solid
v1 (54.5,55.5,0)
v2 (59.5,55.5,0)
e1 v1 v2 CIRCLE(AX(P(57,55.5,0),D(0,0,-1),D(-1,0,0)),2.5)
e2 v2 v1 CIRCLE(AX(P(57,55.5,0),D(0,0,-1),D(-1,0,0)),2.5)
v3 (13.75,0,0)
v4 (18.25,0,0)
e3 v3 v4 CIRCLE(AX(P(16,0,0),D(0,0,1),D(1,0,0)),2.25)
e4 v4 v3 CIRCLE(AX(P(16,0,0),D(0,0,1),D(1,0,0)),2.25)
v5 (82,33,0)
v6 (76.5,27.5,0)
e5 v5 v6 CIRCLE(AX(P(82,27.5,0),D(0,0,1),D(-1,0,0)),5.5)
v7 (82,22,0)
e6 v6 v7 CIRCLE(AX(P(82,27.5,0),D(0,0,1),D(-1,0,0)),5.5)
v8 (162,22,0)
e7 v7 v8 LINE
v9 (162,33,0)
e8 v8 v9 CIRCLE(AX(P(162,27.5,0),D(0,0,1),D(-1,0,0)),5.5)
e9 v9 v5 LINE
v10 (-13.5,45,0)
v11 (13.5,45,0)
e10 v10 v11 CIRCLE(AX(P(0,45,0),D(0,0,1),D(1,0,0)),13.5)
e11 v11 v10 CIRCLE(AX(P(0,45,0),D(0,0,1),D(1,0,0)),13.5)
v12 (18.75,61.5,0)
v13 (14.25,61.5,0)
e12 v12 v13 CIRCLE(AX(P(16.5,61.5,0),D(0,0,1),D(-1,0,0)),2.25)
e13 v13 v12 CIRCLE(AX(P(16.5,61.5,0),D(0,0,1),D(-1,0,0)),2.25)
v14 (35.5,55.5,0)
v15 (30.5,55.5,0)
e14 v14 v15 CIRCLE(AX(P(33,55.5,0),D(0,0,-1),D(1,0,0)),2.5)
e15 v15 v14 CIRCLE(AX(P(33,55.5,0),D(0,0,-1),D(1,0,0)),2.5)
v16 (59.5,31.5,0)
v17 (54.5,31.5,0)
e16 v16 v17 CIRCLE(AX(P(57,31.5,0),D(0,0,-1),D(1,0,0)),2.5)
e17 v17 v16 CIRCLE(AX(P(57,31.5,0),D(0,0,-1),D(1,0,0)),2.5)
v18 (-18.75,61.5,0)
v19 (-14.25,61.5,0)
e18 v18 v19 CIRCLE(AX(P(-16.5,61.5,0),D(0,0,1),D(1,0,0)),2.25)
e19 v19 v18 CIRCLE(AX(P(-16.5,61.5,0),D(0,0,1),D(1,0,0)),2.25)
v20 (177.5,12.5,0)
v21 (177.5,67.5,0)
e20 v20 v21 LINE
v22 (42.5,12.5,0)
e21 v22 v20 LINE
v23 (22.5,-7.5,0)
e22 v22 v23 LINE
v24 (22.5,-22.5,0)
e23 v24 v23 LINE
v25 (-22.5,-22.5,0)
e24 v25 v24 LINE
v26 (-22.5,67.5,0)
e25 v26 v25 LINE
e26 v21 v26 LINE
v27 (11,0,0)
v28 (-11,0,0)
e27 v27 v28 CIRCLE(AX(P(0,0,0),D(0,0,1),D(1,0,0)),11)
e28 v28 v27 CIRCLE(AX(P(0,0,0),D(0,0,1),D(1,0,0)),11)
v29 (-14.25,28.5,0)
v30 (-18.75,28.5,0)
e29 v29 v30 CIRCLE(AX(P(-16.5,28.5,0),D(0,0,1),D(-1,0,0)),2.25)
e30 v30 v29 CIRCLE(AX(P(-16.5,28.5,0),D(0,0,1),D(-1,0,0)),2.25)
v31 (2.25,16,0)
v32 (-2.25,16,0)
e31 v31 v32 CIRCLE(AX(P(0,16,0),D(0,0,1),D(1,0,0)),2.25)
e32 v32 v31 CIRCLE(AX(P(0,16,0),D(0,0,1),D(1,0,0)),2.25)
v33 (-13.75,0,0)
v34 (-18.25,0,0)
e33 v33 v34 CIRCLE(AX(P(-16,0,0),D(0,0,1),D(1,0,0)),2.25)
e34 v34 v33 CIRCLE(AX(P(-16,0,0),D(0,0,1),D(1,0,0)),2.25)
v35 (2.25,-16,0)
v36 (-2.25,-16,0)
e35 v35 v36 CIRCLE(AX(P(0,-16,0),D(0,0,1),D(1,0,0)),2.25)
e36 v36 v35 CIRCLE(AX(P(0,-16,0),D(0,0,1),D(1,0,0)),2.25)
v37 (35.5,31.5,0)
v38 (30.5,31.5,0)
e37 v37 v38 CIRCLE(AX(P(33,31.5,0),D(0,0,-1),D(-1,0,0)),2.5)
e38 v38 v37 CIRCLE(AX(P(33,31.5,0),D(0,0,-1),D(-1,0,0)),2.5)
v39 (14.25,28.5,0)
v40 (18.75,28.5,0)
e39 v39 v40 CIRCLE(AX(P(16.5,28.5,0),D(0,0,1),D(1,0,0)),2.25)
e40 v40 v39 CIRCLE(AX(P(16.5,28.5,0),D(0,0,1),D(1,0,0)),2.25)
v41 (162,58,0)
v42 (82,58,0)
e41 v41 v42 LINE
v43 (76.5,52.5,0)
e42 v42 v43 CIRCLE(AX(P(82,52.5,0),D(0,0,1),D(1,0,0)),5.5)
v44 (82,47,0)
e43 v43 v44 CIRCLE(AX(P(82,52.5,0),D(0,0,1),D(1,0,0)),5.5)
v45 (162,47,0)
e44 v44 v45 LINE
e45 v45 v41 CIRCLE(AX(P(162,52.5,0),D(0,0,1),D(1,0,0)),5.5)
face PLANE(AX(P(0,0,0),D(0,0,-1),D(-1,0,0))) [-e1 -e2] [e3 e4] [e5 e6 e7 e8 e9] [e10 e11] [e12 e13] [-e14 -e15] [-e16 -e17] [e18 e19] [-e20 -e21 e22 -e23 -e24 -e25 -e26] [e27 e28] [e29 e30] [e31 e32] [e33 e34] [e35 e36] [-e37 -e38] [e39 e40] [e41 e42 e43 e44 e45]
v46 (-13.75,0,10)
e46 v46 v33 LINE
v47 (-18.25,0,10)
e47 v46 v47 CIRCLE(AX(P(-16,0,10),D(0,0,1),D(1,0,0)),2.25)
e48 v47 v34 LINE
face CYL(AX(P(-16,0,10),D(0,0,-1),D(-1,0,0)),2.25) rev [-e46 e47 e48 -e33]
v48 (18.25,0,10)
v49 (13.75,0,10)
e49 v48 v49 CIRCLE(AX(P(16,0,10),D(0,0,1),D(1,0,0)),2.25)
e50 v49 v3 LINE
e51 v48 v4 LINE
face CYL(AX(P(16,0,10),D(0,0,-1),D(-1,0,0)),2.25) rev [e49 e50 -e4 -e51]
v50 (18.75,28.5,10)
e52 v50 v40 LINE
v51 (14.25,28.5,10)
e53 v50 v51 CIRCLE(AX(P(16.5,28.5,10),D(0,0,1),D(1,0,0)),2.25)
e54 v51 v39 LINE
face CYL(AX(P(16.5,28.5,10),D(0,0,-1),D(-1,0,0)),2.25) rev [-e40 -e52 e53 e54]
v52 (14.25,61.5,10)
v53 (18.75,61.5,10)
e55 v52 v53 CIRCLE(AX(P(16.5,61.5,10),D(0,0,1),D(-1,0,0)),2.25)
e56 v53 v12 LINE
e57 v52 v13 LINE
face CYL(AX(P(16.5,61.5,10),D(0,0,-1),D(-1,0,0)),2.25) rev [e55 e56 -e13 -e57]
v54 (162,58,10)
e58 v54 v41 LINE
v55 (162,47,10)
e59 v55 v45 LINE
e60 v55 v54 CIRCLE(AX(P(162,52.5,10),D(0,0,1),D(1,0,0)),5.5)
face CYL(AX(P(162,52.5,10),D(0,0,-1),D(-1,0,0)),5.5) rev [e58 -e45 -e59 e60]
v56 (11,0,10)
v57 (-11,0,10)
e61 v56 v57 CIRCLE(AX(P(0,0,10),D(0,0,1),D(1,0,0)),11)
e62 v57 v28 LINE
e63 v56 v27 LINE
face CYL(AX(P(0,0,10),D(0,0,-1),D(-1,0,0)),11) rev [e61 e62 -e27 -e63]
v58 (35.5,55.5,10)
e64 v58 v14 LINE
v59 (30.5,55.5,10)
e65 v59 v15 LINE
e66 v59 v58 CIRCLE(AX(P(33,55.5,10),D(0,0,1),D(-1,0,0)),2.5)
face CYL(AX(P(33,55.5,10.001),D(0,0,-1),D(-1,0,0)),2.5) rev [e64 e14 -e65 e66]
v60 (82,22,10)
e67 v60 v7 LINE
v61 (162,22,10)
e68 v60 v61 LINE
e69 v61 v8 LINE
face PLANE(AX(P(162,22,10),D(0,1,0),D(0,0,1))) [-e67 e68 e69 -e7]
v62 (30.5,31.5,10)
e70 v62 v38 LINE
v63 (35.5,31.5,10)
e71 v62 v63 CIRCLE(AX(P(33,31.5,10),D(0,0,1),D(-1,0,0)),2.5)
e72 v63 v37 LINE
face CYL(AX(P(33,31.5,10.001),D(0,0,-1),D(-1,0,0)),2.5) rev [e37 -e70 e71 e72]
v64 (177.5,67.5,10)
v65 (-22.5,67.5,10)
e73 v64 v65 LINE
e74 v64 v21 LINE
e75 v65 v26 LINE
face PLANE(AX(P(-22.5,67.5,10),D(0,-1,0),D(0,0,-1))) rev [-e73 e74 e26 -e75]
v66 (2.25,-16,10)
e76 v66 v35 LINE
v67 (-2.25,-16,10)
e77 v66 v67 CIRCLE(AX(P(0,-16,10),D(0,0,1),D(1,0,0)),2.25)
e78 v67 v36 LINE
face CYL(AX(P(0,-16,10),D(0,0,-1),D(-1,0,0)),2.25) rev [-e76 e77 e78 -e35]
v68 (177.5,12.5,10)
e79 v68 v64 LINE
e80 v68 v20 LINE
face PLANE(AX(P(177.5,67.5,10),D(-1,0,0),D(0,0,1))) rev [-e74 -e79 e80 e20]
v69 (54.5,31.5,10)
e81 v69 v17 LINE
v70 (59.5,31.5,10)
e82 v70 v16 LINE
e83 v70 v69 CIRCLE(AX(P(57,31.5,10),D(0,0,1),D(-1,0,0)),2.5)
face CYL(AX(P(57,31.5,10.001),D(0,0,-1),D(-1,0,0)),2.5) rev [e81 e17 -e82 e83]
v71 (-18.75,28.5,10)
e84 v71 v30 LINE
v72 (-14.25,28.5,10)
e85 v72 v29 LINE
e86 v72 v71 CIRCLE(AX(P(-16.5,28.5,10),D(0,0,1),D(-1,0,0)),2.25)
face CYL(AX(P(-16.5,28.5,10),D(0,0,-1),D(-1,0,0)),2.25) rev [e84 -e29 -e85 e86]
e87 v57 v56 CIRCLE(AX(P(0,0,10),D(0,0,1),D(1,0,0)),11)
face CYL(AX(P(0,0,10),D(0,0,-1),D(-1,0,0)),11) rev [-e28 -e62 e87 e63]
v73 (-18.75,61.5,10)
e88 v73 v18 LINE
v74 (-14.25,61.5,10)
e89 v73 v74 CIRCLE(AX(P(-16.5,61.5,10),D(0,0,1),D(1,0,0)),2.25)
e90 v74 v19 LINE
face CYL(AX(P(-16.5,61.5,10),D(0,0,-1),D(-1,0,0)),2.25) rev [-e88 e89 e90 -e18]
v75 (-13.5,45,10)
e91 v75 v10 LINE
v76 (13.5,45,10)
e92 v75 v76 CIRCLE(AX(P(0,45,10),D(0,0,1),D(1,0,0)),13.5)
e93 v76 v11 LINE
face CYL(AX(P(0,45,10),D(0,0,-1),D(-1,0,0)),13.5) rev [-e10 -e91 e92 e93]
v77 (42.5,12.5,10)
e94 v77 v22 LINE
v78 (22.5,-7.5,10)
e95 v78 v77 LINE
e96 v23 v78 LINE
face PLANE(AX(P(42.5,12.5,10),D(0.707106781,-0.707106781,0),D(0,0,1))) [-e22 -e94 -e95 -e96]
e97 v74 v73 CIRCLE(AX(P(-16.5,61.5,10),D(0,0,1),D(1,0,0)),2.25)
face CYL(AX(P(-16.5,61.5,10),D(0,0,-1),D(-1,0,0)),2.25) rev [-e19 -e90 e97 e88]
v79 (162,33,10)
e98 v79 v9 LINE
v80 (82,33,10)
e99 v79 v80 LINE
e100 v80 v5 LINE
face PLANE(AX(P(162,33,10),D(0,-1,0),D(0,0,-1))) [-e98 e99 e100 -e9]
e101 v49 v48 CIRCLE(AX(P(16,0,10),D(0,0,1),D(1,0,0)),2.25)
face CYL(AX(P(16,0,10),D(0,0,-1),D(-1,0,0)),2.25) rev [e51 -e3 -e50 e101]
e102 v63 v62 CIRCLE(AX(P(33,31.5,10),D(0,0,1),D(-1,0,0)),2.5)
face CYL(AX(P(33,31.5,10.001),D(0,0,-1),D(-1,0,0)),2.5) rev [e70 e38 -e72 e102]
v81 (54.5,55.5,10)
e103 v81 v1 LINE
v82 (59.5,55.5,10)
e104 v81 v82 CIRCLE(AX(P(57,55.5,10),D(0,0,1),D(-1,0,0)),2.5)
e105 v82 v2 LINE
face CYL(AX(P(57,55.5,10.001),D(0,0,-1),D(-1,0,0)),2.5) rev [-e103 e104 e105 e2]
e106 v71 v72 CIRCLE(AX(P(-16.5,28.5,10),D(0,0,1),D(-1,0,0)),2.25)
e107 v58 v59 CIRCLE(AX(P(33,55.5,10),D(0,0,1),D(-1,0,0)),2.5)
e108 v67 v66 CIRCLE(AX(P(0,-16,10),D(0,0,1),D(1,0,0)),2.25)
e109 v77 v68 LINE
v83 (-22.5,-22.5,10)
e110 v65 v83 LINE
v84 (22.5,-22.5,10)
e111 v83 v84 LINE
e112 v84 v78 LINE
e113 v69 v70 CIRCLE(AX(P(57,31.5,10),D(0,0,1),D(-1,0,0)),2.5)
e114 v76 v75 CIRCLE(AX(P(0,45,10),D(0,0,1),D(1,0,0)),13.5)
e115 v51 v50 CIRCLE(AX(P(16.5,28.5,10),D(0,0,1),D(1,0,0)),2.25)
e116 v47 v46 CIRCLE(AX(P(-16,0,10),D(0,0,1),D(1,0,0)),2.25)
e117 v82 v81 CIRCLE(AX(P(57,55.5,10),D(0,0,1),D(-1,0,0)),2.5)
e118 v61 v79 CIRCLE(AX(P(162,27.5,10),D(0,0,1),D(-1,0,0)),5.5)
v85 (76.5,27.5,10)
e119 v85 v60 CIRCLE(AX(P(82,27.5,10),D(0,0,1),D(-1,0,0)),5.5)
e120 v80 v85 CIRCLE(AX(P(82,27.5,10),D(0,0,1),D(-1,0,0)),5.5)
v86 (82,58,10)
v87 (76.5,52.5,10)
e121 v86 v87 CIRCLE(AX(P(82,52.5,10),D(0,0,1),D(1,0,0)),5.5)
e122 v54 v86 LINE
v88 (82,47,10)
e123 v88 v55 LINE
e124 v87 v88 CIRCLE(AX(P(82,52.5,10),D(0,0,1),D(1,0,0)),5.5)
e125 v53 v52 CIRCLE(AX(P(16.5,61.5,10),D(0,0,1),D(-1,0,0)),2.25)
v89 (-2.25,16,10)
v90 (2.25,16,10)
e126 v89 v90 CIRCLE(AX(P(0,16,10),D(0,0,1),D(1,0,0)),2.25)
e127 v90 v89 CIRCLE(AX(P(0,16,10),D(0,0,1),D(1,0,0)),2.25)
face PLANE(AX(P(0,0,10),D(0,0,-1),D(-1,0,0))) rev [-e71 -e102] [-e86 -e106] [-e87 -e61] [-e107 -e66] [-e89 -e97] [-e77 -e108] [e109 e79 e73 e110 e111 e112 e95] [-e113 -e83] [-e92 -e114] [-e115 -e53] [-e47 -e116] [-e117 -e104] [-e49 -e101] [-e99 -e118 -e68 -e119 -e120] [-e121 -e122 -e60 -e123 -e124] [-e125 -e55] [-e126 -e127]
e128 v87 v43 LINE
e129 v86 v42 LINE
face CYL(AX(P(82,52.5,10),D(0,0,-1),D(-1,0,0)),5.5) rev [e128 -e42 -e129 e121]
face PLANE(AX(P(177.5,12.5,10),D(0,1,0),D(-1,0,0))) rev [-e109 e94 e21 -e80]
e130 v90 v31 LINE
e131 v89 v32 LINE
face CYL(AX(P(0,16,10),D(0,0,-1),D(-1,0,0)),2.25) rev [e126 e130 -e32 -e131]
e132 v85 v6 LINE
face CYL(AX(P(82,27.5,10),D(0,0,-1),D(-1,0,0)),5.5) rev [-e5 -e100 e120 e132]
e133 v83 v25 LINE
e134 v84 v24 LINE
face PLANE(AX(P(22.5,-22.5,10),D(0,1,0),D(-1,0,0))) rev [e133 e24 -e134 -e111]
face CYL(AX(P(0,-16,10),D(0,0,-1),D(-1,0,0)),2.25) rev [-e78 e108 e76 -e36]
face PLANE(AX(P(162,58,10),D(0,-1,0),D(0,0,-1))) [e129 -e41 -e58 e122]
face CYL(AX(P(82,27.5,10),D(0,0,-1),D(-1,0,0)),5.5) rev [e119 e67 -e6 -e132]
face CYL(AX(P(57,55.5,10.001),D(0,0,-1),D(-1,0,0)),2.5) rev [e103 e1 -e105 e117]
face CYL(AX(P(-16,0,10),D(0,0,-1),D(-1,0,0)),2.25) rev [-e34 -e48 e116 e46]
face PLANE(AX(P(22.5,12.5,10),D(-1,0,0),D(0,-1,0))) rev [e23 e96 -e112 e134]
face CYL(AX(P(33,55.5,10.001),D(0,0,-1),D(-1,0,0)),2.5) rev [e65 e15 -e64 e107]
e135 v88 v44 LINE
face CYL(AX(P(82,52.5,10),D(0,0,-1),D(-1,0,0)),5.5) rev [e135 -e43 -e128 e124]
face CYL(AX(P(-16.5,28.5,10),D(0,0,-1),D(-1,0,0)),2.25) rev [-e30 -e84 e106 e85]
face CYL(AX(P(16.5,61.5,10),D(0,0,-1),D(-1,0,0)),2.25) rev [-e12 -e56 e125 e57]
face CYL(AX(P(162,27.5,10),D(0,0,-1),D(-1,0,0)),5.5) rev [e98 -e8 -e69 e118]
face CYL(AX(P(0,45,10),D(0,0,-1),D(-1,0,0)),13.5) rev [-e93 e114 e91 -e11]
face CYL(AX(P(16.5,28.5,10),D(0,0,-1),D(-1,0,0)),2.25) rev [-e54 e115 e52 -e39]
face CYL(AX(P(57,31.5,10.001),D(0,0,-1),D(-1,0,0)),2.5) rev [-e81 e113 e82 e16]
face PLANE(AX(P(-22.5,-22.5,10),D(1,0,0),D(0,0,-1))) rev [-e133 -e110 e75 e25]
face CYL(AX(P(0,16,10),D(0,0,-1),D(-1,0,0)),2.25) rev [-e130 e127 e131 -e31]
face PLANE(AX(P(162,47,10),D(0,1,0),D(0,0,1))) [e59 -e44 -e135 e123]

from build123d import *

# Parameters (mm, degrees)
SKETCH_2_R          = 11
SKETCH_2_R_2        = 13.5
SKETCH_2_R_3        = 2.25
EXTRUDE_1_DEPTH     = 10
CHAMFER_1_SIZE      = 20
CUT_EXTRUDE_1_REACH = 192.164
SKETCH_3_R          = 2.5


with BuildPart() as part:
    # 草图2 → 凸台-拉伸1 (new body)
    with BuildSketch(Plane.XY):
        Polygon((-22.5, 67.5), (177.5, 67.5), (177.5, 12.5), (22.5, 12.5), (22.5, -22.5), (-22.5, -22.5), align=None)
        Circle(SKETCH_2_R, mode=Mode.SUBTRACT)
        with Locations((0, 45)):
            Circle(SKETCH_2_R_2, mode=Mode.SUBTRACT)
        with Locations((-16.5, 61.5)):
            Circle(SKETCH_2_R_3, mode=Mode.SUBTRACT)
        with Locations(Location((16.5, 61.5, 0), (0, 0, 180))):
            Circle(SKETCH_2_R_3, mode=Mode.SUBTRACT)
        with Locations((16.5, 28.5)):
            Circle(SKETCH_2_R_3, mode=Mode.SUBTRACT)
        with Locations(Location((-16.5, 28.5, 0), (0, 0, 180))):
            Circle(SKETCH_2_R_3, mode=Mode.SUBTRACT)
        with Locations((0, 16)):
            Circle(SKETCH_2_R_3, mode=Mode.SUBTRACT)
        with Locations((16, 0)):
            Circle(SKETCH_2_R_3, mode=Mode.SUBTRACT)
        with Locations((0, -16)):
            Circle(SKETCH_2_R_3, mode=Mode.SUBTRACT)
        with Locations((-16, 0)):
            Circle(SKETCH_2_R_3, mode=Mode.SUBTRACT)
        with BuildLine():
            Line((162, 47), (82, 47))
            ThreePointArc((82, 47), (76.5, 52.5), (82, 58))
            Line((82, 58), (162, 58))
            ThreePointArc((162, 58), (167.5, 52.5), (162, 47))
        make_face(mode=Mode.SUBTRACT)
        with BuildLine():
            Line((162, 33), (82, 33))
            ThreePointArc((82, 33), (76.5, 27.5), (82, 22))
            Line((82, 22), (162, 22))
            ThreePointArc((162, 22), (167.5, 27.5), (162, 33))
        make_face(mode=Mode.SUBTRACT)
    extrude(amount=EXTRUDE_1_DEPTH)

    # 倒角1
    chamfer_1_edges = [part.edges().sort_by_distance(p)[0] for p in [
        (22.5, 12.5, 5),
    ]]
    chamfer(chamfer_1_edges, length=CHAMFER_1_SIZE)

    # 草图3 → 切除-拉伸1 (cut, up to next)
    with BuildSketch(Plane(origin=(0, 0, 0), x_dir=(-1, 0, 0), z_dir=(0, 0, -1)), mode=Mode.PRIVATE) as cut_extrude_1_sk1:
        with Locations((-57, 55.5)):
            Circle(SKETCH_3_R)
    cut_extrude_1_tool1 = extrude(cut_extrude_1_sk1.sketch, amount=-CUT_EXTRUDE_1_REACH, mode=Mode.PRIVATE) & part.part
    # 草图3 → 切除-拉伸1 (cut, up to next)
    with BuildSketch(Plane(origin=(0, 0, 0), x_dir=(-1, 0, 0), z_dir=(0, 0, -1)), mode=Mode.PRIVATE) as cut_extrude_1_sk2:
        with Locations((-33, 55.5)):
            Circle(SKETCH_3_R)
    cut_extrude_1_tool2 = extrude(cut_extrude_1_sk2.sketch, amount=-CUT_EXTRUDE_1_REACH, mode=Mode.PRIVATE) & part.part
    # 草图3 → 切除-拉伸1 (cut, up to next)
    with BuildSketch(Plane(origin=(0, 0, 0), x_dir=(-1, 0, 0), z_dir=(0, 0, -1)), mode=Mode.PRIVATE) as cut_extrude_1_sk3:
        with Locations((-33, 31.5)):
            Circle(SKETCH_3_R)
    cut_extrude_1_tool3 = extrude(cut_extrude_1_sk3.sketch, amount=-CUT_EXTRUDE_1_REACH, mode=Mode.PRIVATE) & part.part
    # 草图3 → 切除-拉伸1 (cut, up to next)
    with BuildSketch(Plane(origin=(0, 0, 0), x_dir=(-1, 0, 0), z_dir=(0, 0, -1)), mode=Mode.PRIVATE) as cut_extrude_1_sk4:
        with Locations((-57, 31.5)):
            Circle(SKETCH_3_R)
    cut_extrude_1_tool4 = extrude(cut_extrude_1_sk4.sketch, amount=-CUT_EXTRUDE_1_REACH, mode=Mode.PRIVATE) & part.part
    add(cut_extrude_1_tool1.solids().sort_by_distance((57, 55.5, 0))[0], mode=Mode.SUBTRACT)
    add(cut_extrude_1_tool2.solids().sort_by_distance((33, 55.5, 0))[0], mode=Mode.SUBTRACT)
    add(cut_extrude_1_tool3.solids().sort_by_distance((33, 31.5, 0))[0], mode=Mode.SUBTRACT)
    add(cut_extrude_1_tool4.solids().sort_by_distance((57, 31.5, 0))[0], mode=Mode.SUBTRACT)


solid = part.part
